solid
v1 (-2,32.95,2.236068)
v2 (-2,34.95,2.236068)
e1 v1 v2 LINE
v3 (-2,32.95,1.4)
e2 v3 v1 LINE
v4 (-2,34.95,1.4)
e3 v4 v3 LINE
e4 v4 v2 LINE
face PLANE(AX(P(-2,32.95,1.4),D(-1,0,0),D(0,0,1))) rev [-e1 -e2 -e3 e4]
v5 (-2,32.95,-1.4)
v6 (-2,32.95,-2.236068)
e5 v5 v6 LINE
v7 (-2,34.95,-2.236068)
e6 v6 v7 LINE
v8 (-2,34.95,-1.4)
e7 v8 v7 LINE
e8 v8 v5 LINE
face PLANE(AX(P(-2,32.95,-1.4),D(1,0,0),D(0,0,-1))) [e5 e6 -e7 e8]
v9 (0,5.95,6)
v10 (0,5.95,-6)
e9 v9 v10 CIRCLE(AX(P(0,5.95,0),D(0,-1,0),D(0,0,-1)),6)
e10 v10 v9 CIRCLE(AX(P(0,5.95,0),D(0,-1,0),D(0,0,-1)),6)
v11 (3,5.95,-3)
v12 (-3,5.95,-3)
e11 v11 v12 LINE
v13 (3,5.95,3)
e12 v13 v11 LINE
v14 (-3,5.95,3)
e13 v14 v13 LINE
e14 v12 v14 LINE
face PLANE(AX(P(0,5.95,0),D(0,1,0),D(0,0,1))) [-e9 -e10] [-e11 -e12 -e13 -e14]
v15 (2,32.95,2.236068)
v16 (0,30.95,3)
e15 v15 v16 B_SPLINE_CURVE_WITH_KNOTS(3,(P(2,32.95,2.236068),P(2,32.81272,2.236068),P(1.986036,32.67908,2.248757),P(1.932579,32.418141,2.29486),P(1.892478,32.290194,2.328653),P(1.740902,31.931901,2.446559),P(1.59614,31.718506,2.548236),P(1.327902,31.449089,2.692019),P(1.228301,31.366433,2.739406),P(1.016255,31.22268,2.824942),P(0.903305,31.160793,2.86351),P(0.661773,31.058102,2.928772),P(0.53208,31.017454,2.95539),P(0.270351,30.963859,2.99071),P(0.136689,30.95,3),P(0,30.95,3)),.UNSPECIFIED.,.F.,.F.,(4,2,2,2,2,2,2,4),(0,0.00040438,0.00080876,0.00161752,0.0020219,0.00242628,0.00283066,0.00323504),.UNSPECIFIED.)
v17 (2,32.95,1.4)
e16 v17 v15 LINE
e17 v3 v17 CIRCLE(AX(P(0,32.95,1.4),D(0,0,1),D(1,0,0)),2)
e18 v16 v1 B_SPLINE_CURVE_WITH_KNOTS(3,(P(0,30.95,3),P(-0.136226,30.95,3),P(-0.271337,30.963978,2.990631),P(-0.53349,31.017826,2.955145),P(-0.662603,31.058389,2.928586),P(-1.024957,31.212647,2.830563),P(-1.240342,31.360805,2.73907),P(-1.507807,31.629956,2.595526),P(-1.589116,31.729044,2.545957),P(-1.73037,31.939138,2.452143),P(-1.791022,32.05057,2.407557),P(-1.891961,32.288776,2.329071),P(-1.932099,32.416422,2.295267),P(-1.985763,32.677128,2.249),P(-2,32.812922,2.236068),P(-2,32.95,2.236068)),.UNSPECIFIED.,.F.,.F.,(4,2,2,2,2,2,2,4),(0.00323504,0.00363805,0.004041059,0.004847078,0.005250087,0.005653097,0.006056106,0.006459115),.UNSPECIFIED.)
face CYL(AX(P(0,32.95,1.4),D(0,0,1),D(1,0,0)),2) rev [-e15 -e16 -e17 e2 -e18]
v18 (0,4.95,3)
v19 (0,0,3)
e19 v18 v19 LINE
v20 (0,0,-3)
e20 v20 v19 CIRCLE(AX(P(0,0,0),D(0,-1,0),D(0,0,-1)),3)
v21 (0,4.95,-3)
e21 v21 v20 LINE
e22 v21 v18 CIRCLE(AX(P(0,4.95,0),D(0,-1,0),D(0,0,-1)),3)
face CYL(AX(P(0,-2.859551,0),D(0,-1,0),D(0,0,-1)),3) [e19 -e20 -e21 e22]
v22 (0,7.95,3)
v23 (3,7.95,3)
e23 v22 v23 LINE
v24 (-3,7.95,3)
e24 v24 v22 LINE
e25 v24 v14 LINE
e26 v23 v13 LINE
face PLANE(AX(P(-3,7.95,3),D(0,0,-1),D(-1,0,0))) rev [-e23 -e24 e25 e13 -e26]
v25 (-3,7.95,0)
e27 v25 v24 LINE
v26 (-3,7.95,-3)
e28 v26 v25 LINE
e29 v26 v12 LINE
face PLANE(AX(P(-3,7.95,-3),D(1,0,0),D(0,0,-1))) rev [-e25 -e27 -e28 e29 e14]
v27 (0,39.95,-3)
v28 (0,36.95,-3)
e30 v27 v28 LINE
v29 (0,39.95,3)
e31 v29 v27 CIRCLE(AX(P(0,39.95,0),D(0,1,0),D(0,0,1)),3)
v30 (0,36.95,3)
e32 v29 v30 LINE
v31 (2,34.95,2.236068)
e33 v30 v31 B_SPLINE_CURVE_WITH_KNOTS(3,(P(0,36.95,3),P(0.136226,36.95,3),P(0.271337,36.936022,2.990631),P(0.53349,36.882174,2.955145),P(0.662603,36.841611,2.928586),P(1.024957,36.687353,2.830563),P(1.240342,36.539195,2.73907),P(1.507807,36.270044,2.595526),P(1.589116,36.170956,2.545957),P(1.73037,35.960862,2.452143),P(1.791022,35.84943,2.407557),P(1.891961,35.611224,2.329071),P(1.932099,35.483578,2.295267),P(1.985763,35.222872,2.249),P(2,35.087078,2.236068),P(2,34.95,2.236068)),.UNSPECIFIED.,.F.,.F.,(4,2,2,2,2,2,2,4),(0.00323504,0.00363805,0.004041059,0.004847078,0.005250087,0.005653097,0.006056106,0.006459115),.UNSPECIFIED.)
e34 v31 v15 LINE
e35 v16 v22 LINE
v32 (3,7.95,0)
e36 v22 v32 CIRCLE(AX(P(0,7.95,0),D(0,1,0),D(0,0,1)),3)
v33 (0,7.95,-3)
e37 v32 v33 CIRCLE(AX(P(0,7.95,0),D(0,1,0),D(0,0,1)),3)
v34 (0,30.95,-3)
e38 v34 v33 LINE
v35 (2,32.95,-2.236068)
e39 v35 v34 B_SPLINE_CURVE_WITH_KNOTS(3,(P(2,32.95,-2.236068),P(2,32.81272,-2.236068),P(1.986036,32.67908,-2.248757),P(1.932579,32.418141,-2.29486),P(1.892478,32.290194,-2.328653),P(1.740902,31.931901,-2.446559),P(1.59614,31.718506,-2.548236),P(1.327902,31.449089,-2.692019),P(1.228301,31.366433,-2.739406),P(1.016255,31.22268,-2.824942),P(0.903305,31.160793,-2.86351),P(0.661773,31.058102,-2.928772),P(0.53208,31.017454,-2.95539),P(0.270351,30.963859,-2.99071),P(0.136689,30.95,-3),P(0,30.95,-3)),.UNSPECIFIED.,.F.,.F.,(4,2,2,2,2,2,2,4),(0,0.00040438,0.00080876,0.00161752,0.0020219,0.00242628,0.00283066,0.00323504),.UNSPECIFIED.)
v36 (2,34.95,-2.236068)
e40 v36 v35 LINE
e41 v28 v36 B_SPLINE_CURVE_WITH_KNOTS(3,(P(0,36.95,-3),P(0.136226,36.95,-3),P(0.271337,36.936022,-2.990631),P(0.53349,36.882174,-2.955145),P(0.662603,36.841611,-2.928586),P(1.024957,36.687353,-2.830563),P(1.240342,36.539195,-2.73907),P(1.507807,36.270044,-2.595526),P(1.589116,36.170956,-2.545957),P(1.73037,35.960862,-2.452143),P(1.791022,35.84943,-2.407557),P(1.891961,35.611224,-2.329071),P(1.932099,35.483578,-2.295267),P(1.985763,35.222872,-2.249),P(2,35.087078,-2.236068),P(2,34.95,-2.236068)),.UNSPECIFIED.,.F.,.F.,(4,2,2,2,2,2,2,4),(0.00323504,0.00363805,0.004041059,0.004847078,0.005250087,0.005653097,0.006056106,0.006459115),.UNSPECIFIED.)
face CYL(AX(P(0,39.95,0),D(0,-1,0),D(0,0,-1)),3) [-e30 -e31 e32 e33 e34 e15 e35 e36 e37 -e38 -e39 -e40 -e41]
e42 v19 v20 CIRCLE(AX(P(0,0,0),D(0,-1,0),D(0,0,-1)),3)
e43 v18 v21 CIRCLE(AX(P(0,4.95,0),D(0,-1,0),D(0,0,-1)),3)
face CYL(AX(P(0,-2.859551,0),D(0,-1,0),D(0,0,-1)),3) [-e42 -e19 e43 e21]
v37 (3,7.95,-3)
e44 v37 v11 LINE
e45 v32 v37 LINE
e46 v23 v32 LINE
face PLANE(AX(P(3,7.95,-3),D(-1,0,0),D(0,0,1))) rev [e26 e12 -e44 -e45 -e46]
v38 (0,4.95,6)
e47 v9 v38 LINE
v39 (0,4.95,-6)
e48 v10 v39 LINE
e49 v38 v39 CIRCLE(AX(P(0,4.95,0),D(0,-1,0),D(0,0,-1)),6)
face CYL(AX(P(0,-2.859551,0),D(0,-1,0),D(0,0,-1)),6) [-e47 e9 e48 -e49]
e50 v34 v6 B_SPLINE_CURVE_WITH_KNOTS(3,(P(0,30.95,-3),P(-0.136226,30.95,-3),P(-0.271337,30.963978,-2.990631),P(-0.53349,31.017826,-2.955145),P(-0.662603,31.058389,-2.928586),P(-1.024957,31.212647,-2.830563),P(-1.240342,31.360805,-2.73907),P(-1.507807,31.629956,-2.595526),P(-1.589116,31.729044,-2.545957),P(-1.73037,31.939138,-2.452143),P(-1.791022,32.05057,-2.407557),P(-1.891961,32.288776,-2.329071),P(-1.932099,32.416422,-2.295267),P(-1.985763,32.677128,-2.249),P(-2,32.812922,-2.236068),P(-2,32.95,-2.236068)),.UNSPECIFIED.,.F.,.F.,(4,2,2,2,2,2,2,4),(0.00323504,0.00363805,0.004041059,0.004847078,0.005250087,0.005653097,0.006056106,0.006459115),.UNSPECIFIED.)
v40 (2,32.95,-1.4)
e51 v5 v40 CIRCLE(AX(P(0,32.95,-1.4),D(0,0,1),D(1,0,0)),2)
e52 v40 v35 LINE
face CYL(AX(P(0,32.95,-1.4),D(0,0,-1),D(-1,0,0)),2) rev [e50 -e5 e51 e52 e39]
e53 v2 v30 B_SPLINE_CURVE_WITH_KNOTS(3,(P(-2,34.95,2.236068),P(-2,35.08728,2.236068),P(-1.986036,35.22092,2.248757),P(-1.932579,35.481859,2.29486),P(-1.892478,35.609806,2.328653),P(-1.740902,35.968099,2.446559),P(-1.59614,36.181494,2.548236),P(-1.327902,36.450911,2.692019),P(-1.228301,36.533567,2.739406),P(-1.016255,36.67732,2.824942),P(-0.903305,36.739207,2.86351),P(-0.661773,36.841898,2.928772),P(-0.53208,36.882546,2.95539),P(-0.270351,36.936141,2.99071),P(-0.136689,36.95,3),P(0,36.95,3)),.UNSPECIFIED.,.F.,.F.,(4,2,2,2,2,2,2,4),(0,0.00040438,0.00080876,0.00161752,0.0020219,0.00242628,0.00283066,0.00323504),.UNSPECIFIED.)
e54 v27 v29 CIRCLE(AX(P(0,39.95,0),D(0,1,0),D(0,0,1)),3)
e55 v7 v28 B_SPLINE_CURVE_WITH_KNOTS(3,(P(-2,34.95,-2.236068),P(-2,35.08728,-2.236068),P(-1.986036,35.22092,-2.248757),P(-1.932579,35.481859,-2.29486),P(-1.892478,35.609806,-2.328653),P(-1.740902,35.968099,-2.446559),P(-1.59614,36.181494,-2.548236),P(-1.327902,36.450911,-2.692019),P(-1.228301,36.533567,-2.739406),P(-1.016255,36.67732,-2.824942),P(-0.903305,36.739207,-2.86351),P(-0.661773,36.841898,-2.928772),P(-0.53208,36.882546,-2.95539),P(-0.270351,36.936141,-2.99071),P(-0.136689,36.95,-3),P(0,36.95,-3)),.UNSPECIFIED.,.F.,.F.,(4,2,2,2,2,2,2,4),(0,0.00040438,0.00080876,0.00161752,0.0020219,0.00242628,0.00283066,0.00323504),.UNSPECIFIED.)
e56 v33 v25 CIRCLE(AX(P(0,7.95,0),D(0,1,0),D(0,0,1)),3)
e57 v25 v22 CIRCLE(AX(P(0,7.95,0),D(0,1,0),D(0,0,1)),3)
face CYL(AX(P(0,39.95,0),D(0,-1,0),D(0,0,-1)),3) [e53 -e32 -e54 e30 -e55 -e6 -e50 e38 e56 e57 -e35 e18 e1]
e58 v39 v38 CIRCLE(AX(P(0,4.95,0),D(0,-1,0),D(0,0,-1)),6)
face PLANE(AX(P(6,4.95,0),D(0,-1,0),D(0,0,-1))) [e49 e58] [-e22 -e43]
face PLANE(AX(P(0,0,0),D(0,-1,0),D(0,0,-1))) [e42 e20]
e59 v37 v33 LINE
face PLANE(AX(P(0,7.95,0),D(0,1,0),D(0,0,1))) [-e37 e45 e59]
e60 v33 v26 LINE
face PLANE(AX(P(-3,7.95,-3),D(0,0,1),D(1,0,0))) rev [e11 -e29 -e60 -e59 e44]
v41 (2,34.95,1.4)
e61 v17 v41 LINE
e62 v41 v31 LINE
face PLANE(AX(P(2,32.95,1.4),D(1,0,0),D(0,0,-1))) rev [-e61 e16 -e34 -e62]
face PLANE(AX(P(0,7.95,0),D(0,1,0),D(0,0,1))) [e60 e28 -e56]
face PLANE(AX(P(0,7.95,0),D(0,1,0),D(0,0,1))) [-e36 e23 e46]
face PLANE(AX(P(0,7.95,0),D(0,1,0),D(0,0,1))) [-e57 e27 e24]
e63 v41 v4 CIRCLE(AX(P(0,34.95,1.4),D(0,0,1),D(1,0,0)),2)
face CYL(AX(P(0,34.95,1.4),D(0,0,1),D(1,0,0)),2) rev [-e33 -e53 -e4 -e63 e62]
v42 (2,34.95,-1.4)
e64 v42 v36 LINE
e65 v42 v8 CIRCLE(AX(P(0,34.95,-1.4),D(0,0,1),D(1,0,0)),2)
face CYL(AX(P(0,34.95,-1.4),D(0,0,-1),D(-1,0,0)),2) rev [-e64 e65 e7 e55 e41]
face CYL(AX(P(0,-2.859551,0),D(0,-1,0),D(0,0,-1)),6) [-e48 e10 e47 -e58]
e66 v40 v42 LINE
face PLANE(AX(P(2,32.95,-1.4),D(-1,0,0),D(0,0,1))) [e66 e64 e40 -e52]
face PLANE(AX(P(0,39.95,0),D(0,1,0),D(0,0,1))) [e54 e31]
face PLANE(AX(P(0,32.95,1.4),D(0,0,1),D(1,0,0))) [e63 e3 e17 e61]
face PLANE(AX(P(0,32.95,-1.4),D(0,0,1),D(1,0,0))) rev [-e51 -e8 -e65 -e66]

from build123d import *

# Parameters (mm, degrees)
SKETCH2_W           = 6
SKETCH2_H           = 6
BOSS_EXTRUDE1_DEPTH = 2
BOSS_EXTRUDE2_START = 32
SKETCH3_R           = 3
BOSS_EXTRUDE2_DEPTH = 32
CUT_EXTRUDE2_START  = 3
CUT_EXTRUDE2_DEPTH  = 1.6
CUT_EXTRUDE3_START  = -1.4
CUT_EXTRUDE3_DEPTH  = 1.6


with BuildPart() as part:
    # Sketch1 → Revolve1 (revolve)
    with BuildSketch(Plane.XY, mode=Mode.PRIVATE) as revolve1_sk:
        Polygon((0, 0), (3, 0), (3, 4.95), (6, 4.95), (6, 5.95), (0, 5.95), align=None)
    revolve(revolve1_sk.sketch.rotate(Axis((0, -2.859551482, 0), (0, 1, 0)), 90), axis=Axis((0, -2.859551482, 0), (0, 1, 0)))

    # Sketch2 → Boss-Extrude1 (add)
    with BuildSketch(Plane(origin=(0, 5.95, 0), x_dir=(1, 0, 0), z_dir=(0, 1, 0))):
        Rectangle(SKETCH2_W, SKETCH2_H)
    extrude(amount=BOSS_EXTRUDE1_DEPTH)

    # Sketch3 → Boss-Extrude2 (add)
    with BuildSketch(Plane(origin=(0, 7.95, 0), x_dir=(1, 0, 0), z_dir=(0, 1, 0)).offset(BOSS_EXTRUDE2_START)):
        with Locations(Location((0, 0, 0), (0, 0, 90))):
            Circle(SKETCH3_R)
    extrude(amount=-BOSS_EXTRUDE2_DEPTH)

    # Sketch 4_2 → Cut-Extrude2 (cut)
    with BuildSketch(Plane.XY.offset(CUT_EXTRUDE2_START)):
        with BuildLine():
            Line((-2, 32.95), (-2, 34.95))
            ThreePointArc((-2, 34.95), (0, 36.95), (2, 34.95))
            Line((2, 34.95), (2, 32.95))
            ThreePointArc((2, 32.95), (0, 30.95), (-2, 32.95))
        make_face()
    extrude(amount=-CUT_EXTRUDE2_DEPTH, mode=Mode.SUBTRACT)

    # Sketch 4_2 2 → Cut-Extrude3 (cut)
    with BuildSketch(Plane.XY.offset(CUT_EXTRUDE3_START)):
        with BuildLine():
            Line((-2, 32.95), (-2, 34.95))
            ThreePointArc((-2, 34.95), (0, 36.95), (2, 34.95))
            Line((2, 34.95), (2, 32.95))
            ThreePointArc((2, 32.95), (0, 30.95), (-2, 32.95))
        make_face()
    extrude(amount=-CUT_EXTRUDE3_DEPTH, mode=Mode.SUBTRACT)


solid = part.part
